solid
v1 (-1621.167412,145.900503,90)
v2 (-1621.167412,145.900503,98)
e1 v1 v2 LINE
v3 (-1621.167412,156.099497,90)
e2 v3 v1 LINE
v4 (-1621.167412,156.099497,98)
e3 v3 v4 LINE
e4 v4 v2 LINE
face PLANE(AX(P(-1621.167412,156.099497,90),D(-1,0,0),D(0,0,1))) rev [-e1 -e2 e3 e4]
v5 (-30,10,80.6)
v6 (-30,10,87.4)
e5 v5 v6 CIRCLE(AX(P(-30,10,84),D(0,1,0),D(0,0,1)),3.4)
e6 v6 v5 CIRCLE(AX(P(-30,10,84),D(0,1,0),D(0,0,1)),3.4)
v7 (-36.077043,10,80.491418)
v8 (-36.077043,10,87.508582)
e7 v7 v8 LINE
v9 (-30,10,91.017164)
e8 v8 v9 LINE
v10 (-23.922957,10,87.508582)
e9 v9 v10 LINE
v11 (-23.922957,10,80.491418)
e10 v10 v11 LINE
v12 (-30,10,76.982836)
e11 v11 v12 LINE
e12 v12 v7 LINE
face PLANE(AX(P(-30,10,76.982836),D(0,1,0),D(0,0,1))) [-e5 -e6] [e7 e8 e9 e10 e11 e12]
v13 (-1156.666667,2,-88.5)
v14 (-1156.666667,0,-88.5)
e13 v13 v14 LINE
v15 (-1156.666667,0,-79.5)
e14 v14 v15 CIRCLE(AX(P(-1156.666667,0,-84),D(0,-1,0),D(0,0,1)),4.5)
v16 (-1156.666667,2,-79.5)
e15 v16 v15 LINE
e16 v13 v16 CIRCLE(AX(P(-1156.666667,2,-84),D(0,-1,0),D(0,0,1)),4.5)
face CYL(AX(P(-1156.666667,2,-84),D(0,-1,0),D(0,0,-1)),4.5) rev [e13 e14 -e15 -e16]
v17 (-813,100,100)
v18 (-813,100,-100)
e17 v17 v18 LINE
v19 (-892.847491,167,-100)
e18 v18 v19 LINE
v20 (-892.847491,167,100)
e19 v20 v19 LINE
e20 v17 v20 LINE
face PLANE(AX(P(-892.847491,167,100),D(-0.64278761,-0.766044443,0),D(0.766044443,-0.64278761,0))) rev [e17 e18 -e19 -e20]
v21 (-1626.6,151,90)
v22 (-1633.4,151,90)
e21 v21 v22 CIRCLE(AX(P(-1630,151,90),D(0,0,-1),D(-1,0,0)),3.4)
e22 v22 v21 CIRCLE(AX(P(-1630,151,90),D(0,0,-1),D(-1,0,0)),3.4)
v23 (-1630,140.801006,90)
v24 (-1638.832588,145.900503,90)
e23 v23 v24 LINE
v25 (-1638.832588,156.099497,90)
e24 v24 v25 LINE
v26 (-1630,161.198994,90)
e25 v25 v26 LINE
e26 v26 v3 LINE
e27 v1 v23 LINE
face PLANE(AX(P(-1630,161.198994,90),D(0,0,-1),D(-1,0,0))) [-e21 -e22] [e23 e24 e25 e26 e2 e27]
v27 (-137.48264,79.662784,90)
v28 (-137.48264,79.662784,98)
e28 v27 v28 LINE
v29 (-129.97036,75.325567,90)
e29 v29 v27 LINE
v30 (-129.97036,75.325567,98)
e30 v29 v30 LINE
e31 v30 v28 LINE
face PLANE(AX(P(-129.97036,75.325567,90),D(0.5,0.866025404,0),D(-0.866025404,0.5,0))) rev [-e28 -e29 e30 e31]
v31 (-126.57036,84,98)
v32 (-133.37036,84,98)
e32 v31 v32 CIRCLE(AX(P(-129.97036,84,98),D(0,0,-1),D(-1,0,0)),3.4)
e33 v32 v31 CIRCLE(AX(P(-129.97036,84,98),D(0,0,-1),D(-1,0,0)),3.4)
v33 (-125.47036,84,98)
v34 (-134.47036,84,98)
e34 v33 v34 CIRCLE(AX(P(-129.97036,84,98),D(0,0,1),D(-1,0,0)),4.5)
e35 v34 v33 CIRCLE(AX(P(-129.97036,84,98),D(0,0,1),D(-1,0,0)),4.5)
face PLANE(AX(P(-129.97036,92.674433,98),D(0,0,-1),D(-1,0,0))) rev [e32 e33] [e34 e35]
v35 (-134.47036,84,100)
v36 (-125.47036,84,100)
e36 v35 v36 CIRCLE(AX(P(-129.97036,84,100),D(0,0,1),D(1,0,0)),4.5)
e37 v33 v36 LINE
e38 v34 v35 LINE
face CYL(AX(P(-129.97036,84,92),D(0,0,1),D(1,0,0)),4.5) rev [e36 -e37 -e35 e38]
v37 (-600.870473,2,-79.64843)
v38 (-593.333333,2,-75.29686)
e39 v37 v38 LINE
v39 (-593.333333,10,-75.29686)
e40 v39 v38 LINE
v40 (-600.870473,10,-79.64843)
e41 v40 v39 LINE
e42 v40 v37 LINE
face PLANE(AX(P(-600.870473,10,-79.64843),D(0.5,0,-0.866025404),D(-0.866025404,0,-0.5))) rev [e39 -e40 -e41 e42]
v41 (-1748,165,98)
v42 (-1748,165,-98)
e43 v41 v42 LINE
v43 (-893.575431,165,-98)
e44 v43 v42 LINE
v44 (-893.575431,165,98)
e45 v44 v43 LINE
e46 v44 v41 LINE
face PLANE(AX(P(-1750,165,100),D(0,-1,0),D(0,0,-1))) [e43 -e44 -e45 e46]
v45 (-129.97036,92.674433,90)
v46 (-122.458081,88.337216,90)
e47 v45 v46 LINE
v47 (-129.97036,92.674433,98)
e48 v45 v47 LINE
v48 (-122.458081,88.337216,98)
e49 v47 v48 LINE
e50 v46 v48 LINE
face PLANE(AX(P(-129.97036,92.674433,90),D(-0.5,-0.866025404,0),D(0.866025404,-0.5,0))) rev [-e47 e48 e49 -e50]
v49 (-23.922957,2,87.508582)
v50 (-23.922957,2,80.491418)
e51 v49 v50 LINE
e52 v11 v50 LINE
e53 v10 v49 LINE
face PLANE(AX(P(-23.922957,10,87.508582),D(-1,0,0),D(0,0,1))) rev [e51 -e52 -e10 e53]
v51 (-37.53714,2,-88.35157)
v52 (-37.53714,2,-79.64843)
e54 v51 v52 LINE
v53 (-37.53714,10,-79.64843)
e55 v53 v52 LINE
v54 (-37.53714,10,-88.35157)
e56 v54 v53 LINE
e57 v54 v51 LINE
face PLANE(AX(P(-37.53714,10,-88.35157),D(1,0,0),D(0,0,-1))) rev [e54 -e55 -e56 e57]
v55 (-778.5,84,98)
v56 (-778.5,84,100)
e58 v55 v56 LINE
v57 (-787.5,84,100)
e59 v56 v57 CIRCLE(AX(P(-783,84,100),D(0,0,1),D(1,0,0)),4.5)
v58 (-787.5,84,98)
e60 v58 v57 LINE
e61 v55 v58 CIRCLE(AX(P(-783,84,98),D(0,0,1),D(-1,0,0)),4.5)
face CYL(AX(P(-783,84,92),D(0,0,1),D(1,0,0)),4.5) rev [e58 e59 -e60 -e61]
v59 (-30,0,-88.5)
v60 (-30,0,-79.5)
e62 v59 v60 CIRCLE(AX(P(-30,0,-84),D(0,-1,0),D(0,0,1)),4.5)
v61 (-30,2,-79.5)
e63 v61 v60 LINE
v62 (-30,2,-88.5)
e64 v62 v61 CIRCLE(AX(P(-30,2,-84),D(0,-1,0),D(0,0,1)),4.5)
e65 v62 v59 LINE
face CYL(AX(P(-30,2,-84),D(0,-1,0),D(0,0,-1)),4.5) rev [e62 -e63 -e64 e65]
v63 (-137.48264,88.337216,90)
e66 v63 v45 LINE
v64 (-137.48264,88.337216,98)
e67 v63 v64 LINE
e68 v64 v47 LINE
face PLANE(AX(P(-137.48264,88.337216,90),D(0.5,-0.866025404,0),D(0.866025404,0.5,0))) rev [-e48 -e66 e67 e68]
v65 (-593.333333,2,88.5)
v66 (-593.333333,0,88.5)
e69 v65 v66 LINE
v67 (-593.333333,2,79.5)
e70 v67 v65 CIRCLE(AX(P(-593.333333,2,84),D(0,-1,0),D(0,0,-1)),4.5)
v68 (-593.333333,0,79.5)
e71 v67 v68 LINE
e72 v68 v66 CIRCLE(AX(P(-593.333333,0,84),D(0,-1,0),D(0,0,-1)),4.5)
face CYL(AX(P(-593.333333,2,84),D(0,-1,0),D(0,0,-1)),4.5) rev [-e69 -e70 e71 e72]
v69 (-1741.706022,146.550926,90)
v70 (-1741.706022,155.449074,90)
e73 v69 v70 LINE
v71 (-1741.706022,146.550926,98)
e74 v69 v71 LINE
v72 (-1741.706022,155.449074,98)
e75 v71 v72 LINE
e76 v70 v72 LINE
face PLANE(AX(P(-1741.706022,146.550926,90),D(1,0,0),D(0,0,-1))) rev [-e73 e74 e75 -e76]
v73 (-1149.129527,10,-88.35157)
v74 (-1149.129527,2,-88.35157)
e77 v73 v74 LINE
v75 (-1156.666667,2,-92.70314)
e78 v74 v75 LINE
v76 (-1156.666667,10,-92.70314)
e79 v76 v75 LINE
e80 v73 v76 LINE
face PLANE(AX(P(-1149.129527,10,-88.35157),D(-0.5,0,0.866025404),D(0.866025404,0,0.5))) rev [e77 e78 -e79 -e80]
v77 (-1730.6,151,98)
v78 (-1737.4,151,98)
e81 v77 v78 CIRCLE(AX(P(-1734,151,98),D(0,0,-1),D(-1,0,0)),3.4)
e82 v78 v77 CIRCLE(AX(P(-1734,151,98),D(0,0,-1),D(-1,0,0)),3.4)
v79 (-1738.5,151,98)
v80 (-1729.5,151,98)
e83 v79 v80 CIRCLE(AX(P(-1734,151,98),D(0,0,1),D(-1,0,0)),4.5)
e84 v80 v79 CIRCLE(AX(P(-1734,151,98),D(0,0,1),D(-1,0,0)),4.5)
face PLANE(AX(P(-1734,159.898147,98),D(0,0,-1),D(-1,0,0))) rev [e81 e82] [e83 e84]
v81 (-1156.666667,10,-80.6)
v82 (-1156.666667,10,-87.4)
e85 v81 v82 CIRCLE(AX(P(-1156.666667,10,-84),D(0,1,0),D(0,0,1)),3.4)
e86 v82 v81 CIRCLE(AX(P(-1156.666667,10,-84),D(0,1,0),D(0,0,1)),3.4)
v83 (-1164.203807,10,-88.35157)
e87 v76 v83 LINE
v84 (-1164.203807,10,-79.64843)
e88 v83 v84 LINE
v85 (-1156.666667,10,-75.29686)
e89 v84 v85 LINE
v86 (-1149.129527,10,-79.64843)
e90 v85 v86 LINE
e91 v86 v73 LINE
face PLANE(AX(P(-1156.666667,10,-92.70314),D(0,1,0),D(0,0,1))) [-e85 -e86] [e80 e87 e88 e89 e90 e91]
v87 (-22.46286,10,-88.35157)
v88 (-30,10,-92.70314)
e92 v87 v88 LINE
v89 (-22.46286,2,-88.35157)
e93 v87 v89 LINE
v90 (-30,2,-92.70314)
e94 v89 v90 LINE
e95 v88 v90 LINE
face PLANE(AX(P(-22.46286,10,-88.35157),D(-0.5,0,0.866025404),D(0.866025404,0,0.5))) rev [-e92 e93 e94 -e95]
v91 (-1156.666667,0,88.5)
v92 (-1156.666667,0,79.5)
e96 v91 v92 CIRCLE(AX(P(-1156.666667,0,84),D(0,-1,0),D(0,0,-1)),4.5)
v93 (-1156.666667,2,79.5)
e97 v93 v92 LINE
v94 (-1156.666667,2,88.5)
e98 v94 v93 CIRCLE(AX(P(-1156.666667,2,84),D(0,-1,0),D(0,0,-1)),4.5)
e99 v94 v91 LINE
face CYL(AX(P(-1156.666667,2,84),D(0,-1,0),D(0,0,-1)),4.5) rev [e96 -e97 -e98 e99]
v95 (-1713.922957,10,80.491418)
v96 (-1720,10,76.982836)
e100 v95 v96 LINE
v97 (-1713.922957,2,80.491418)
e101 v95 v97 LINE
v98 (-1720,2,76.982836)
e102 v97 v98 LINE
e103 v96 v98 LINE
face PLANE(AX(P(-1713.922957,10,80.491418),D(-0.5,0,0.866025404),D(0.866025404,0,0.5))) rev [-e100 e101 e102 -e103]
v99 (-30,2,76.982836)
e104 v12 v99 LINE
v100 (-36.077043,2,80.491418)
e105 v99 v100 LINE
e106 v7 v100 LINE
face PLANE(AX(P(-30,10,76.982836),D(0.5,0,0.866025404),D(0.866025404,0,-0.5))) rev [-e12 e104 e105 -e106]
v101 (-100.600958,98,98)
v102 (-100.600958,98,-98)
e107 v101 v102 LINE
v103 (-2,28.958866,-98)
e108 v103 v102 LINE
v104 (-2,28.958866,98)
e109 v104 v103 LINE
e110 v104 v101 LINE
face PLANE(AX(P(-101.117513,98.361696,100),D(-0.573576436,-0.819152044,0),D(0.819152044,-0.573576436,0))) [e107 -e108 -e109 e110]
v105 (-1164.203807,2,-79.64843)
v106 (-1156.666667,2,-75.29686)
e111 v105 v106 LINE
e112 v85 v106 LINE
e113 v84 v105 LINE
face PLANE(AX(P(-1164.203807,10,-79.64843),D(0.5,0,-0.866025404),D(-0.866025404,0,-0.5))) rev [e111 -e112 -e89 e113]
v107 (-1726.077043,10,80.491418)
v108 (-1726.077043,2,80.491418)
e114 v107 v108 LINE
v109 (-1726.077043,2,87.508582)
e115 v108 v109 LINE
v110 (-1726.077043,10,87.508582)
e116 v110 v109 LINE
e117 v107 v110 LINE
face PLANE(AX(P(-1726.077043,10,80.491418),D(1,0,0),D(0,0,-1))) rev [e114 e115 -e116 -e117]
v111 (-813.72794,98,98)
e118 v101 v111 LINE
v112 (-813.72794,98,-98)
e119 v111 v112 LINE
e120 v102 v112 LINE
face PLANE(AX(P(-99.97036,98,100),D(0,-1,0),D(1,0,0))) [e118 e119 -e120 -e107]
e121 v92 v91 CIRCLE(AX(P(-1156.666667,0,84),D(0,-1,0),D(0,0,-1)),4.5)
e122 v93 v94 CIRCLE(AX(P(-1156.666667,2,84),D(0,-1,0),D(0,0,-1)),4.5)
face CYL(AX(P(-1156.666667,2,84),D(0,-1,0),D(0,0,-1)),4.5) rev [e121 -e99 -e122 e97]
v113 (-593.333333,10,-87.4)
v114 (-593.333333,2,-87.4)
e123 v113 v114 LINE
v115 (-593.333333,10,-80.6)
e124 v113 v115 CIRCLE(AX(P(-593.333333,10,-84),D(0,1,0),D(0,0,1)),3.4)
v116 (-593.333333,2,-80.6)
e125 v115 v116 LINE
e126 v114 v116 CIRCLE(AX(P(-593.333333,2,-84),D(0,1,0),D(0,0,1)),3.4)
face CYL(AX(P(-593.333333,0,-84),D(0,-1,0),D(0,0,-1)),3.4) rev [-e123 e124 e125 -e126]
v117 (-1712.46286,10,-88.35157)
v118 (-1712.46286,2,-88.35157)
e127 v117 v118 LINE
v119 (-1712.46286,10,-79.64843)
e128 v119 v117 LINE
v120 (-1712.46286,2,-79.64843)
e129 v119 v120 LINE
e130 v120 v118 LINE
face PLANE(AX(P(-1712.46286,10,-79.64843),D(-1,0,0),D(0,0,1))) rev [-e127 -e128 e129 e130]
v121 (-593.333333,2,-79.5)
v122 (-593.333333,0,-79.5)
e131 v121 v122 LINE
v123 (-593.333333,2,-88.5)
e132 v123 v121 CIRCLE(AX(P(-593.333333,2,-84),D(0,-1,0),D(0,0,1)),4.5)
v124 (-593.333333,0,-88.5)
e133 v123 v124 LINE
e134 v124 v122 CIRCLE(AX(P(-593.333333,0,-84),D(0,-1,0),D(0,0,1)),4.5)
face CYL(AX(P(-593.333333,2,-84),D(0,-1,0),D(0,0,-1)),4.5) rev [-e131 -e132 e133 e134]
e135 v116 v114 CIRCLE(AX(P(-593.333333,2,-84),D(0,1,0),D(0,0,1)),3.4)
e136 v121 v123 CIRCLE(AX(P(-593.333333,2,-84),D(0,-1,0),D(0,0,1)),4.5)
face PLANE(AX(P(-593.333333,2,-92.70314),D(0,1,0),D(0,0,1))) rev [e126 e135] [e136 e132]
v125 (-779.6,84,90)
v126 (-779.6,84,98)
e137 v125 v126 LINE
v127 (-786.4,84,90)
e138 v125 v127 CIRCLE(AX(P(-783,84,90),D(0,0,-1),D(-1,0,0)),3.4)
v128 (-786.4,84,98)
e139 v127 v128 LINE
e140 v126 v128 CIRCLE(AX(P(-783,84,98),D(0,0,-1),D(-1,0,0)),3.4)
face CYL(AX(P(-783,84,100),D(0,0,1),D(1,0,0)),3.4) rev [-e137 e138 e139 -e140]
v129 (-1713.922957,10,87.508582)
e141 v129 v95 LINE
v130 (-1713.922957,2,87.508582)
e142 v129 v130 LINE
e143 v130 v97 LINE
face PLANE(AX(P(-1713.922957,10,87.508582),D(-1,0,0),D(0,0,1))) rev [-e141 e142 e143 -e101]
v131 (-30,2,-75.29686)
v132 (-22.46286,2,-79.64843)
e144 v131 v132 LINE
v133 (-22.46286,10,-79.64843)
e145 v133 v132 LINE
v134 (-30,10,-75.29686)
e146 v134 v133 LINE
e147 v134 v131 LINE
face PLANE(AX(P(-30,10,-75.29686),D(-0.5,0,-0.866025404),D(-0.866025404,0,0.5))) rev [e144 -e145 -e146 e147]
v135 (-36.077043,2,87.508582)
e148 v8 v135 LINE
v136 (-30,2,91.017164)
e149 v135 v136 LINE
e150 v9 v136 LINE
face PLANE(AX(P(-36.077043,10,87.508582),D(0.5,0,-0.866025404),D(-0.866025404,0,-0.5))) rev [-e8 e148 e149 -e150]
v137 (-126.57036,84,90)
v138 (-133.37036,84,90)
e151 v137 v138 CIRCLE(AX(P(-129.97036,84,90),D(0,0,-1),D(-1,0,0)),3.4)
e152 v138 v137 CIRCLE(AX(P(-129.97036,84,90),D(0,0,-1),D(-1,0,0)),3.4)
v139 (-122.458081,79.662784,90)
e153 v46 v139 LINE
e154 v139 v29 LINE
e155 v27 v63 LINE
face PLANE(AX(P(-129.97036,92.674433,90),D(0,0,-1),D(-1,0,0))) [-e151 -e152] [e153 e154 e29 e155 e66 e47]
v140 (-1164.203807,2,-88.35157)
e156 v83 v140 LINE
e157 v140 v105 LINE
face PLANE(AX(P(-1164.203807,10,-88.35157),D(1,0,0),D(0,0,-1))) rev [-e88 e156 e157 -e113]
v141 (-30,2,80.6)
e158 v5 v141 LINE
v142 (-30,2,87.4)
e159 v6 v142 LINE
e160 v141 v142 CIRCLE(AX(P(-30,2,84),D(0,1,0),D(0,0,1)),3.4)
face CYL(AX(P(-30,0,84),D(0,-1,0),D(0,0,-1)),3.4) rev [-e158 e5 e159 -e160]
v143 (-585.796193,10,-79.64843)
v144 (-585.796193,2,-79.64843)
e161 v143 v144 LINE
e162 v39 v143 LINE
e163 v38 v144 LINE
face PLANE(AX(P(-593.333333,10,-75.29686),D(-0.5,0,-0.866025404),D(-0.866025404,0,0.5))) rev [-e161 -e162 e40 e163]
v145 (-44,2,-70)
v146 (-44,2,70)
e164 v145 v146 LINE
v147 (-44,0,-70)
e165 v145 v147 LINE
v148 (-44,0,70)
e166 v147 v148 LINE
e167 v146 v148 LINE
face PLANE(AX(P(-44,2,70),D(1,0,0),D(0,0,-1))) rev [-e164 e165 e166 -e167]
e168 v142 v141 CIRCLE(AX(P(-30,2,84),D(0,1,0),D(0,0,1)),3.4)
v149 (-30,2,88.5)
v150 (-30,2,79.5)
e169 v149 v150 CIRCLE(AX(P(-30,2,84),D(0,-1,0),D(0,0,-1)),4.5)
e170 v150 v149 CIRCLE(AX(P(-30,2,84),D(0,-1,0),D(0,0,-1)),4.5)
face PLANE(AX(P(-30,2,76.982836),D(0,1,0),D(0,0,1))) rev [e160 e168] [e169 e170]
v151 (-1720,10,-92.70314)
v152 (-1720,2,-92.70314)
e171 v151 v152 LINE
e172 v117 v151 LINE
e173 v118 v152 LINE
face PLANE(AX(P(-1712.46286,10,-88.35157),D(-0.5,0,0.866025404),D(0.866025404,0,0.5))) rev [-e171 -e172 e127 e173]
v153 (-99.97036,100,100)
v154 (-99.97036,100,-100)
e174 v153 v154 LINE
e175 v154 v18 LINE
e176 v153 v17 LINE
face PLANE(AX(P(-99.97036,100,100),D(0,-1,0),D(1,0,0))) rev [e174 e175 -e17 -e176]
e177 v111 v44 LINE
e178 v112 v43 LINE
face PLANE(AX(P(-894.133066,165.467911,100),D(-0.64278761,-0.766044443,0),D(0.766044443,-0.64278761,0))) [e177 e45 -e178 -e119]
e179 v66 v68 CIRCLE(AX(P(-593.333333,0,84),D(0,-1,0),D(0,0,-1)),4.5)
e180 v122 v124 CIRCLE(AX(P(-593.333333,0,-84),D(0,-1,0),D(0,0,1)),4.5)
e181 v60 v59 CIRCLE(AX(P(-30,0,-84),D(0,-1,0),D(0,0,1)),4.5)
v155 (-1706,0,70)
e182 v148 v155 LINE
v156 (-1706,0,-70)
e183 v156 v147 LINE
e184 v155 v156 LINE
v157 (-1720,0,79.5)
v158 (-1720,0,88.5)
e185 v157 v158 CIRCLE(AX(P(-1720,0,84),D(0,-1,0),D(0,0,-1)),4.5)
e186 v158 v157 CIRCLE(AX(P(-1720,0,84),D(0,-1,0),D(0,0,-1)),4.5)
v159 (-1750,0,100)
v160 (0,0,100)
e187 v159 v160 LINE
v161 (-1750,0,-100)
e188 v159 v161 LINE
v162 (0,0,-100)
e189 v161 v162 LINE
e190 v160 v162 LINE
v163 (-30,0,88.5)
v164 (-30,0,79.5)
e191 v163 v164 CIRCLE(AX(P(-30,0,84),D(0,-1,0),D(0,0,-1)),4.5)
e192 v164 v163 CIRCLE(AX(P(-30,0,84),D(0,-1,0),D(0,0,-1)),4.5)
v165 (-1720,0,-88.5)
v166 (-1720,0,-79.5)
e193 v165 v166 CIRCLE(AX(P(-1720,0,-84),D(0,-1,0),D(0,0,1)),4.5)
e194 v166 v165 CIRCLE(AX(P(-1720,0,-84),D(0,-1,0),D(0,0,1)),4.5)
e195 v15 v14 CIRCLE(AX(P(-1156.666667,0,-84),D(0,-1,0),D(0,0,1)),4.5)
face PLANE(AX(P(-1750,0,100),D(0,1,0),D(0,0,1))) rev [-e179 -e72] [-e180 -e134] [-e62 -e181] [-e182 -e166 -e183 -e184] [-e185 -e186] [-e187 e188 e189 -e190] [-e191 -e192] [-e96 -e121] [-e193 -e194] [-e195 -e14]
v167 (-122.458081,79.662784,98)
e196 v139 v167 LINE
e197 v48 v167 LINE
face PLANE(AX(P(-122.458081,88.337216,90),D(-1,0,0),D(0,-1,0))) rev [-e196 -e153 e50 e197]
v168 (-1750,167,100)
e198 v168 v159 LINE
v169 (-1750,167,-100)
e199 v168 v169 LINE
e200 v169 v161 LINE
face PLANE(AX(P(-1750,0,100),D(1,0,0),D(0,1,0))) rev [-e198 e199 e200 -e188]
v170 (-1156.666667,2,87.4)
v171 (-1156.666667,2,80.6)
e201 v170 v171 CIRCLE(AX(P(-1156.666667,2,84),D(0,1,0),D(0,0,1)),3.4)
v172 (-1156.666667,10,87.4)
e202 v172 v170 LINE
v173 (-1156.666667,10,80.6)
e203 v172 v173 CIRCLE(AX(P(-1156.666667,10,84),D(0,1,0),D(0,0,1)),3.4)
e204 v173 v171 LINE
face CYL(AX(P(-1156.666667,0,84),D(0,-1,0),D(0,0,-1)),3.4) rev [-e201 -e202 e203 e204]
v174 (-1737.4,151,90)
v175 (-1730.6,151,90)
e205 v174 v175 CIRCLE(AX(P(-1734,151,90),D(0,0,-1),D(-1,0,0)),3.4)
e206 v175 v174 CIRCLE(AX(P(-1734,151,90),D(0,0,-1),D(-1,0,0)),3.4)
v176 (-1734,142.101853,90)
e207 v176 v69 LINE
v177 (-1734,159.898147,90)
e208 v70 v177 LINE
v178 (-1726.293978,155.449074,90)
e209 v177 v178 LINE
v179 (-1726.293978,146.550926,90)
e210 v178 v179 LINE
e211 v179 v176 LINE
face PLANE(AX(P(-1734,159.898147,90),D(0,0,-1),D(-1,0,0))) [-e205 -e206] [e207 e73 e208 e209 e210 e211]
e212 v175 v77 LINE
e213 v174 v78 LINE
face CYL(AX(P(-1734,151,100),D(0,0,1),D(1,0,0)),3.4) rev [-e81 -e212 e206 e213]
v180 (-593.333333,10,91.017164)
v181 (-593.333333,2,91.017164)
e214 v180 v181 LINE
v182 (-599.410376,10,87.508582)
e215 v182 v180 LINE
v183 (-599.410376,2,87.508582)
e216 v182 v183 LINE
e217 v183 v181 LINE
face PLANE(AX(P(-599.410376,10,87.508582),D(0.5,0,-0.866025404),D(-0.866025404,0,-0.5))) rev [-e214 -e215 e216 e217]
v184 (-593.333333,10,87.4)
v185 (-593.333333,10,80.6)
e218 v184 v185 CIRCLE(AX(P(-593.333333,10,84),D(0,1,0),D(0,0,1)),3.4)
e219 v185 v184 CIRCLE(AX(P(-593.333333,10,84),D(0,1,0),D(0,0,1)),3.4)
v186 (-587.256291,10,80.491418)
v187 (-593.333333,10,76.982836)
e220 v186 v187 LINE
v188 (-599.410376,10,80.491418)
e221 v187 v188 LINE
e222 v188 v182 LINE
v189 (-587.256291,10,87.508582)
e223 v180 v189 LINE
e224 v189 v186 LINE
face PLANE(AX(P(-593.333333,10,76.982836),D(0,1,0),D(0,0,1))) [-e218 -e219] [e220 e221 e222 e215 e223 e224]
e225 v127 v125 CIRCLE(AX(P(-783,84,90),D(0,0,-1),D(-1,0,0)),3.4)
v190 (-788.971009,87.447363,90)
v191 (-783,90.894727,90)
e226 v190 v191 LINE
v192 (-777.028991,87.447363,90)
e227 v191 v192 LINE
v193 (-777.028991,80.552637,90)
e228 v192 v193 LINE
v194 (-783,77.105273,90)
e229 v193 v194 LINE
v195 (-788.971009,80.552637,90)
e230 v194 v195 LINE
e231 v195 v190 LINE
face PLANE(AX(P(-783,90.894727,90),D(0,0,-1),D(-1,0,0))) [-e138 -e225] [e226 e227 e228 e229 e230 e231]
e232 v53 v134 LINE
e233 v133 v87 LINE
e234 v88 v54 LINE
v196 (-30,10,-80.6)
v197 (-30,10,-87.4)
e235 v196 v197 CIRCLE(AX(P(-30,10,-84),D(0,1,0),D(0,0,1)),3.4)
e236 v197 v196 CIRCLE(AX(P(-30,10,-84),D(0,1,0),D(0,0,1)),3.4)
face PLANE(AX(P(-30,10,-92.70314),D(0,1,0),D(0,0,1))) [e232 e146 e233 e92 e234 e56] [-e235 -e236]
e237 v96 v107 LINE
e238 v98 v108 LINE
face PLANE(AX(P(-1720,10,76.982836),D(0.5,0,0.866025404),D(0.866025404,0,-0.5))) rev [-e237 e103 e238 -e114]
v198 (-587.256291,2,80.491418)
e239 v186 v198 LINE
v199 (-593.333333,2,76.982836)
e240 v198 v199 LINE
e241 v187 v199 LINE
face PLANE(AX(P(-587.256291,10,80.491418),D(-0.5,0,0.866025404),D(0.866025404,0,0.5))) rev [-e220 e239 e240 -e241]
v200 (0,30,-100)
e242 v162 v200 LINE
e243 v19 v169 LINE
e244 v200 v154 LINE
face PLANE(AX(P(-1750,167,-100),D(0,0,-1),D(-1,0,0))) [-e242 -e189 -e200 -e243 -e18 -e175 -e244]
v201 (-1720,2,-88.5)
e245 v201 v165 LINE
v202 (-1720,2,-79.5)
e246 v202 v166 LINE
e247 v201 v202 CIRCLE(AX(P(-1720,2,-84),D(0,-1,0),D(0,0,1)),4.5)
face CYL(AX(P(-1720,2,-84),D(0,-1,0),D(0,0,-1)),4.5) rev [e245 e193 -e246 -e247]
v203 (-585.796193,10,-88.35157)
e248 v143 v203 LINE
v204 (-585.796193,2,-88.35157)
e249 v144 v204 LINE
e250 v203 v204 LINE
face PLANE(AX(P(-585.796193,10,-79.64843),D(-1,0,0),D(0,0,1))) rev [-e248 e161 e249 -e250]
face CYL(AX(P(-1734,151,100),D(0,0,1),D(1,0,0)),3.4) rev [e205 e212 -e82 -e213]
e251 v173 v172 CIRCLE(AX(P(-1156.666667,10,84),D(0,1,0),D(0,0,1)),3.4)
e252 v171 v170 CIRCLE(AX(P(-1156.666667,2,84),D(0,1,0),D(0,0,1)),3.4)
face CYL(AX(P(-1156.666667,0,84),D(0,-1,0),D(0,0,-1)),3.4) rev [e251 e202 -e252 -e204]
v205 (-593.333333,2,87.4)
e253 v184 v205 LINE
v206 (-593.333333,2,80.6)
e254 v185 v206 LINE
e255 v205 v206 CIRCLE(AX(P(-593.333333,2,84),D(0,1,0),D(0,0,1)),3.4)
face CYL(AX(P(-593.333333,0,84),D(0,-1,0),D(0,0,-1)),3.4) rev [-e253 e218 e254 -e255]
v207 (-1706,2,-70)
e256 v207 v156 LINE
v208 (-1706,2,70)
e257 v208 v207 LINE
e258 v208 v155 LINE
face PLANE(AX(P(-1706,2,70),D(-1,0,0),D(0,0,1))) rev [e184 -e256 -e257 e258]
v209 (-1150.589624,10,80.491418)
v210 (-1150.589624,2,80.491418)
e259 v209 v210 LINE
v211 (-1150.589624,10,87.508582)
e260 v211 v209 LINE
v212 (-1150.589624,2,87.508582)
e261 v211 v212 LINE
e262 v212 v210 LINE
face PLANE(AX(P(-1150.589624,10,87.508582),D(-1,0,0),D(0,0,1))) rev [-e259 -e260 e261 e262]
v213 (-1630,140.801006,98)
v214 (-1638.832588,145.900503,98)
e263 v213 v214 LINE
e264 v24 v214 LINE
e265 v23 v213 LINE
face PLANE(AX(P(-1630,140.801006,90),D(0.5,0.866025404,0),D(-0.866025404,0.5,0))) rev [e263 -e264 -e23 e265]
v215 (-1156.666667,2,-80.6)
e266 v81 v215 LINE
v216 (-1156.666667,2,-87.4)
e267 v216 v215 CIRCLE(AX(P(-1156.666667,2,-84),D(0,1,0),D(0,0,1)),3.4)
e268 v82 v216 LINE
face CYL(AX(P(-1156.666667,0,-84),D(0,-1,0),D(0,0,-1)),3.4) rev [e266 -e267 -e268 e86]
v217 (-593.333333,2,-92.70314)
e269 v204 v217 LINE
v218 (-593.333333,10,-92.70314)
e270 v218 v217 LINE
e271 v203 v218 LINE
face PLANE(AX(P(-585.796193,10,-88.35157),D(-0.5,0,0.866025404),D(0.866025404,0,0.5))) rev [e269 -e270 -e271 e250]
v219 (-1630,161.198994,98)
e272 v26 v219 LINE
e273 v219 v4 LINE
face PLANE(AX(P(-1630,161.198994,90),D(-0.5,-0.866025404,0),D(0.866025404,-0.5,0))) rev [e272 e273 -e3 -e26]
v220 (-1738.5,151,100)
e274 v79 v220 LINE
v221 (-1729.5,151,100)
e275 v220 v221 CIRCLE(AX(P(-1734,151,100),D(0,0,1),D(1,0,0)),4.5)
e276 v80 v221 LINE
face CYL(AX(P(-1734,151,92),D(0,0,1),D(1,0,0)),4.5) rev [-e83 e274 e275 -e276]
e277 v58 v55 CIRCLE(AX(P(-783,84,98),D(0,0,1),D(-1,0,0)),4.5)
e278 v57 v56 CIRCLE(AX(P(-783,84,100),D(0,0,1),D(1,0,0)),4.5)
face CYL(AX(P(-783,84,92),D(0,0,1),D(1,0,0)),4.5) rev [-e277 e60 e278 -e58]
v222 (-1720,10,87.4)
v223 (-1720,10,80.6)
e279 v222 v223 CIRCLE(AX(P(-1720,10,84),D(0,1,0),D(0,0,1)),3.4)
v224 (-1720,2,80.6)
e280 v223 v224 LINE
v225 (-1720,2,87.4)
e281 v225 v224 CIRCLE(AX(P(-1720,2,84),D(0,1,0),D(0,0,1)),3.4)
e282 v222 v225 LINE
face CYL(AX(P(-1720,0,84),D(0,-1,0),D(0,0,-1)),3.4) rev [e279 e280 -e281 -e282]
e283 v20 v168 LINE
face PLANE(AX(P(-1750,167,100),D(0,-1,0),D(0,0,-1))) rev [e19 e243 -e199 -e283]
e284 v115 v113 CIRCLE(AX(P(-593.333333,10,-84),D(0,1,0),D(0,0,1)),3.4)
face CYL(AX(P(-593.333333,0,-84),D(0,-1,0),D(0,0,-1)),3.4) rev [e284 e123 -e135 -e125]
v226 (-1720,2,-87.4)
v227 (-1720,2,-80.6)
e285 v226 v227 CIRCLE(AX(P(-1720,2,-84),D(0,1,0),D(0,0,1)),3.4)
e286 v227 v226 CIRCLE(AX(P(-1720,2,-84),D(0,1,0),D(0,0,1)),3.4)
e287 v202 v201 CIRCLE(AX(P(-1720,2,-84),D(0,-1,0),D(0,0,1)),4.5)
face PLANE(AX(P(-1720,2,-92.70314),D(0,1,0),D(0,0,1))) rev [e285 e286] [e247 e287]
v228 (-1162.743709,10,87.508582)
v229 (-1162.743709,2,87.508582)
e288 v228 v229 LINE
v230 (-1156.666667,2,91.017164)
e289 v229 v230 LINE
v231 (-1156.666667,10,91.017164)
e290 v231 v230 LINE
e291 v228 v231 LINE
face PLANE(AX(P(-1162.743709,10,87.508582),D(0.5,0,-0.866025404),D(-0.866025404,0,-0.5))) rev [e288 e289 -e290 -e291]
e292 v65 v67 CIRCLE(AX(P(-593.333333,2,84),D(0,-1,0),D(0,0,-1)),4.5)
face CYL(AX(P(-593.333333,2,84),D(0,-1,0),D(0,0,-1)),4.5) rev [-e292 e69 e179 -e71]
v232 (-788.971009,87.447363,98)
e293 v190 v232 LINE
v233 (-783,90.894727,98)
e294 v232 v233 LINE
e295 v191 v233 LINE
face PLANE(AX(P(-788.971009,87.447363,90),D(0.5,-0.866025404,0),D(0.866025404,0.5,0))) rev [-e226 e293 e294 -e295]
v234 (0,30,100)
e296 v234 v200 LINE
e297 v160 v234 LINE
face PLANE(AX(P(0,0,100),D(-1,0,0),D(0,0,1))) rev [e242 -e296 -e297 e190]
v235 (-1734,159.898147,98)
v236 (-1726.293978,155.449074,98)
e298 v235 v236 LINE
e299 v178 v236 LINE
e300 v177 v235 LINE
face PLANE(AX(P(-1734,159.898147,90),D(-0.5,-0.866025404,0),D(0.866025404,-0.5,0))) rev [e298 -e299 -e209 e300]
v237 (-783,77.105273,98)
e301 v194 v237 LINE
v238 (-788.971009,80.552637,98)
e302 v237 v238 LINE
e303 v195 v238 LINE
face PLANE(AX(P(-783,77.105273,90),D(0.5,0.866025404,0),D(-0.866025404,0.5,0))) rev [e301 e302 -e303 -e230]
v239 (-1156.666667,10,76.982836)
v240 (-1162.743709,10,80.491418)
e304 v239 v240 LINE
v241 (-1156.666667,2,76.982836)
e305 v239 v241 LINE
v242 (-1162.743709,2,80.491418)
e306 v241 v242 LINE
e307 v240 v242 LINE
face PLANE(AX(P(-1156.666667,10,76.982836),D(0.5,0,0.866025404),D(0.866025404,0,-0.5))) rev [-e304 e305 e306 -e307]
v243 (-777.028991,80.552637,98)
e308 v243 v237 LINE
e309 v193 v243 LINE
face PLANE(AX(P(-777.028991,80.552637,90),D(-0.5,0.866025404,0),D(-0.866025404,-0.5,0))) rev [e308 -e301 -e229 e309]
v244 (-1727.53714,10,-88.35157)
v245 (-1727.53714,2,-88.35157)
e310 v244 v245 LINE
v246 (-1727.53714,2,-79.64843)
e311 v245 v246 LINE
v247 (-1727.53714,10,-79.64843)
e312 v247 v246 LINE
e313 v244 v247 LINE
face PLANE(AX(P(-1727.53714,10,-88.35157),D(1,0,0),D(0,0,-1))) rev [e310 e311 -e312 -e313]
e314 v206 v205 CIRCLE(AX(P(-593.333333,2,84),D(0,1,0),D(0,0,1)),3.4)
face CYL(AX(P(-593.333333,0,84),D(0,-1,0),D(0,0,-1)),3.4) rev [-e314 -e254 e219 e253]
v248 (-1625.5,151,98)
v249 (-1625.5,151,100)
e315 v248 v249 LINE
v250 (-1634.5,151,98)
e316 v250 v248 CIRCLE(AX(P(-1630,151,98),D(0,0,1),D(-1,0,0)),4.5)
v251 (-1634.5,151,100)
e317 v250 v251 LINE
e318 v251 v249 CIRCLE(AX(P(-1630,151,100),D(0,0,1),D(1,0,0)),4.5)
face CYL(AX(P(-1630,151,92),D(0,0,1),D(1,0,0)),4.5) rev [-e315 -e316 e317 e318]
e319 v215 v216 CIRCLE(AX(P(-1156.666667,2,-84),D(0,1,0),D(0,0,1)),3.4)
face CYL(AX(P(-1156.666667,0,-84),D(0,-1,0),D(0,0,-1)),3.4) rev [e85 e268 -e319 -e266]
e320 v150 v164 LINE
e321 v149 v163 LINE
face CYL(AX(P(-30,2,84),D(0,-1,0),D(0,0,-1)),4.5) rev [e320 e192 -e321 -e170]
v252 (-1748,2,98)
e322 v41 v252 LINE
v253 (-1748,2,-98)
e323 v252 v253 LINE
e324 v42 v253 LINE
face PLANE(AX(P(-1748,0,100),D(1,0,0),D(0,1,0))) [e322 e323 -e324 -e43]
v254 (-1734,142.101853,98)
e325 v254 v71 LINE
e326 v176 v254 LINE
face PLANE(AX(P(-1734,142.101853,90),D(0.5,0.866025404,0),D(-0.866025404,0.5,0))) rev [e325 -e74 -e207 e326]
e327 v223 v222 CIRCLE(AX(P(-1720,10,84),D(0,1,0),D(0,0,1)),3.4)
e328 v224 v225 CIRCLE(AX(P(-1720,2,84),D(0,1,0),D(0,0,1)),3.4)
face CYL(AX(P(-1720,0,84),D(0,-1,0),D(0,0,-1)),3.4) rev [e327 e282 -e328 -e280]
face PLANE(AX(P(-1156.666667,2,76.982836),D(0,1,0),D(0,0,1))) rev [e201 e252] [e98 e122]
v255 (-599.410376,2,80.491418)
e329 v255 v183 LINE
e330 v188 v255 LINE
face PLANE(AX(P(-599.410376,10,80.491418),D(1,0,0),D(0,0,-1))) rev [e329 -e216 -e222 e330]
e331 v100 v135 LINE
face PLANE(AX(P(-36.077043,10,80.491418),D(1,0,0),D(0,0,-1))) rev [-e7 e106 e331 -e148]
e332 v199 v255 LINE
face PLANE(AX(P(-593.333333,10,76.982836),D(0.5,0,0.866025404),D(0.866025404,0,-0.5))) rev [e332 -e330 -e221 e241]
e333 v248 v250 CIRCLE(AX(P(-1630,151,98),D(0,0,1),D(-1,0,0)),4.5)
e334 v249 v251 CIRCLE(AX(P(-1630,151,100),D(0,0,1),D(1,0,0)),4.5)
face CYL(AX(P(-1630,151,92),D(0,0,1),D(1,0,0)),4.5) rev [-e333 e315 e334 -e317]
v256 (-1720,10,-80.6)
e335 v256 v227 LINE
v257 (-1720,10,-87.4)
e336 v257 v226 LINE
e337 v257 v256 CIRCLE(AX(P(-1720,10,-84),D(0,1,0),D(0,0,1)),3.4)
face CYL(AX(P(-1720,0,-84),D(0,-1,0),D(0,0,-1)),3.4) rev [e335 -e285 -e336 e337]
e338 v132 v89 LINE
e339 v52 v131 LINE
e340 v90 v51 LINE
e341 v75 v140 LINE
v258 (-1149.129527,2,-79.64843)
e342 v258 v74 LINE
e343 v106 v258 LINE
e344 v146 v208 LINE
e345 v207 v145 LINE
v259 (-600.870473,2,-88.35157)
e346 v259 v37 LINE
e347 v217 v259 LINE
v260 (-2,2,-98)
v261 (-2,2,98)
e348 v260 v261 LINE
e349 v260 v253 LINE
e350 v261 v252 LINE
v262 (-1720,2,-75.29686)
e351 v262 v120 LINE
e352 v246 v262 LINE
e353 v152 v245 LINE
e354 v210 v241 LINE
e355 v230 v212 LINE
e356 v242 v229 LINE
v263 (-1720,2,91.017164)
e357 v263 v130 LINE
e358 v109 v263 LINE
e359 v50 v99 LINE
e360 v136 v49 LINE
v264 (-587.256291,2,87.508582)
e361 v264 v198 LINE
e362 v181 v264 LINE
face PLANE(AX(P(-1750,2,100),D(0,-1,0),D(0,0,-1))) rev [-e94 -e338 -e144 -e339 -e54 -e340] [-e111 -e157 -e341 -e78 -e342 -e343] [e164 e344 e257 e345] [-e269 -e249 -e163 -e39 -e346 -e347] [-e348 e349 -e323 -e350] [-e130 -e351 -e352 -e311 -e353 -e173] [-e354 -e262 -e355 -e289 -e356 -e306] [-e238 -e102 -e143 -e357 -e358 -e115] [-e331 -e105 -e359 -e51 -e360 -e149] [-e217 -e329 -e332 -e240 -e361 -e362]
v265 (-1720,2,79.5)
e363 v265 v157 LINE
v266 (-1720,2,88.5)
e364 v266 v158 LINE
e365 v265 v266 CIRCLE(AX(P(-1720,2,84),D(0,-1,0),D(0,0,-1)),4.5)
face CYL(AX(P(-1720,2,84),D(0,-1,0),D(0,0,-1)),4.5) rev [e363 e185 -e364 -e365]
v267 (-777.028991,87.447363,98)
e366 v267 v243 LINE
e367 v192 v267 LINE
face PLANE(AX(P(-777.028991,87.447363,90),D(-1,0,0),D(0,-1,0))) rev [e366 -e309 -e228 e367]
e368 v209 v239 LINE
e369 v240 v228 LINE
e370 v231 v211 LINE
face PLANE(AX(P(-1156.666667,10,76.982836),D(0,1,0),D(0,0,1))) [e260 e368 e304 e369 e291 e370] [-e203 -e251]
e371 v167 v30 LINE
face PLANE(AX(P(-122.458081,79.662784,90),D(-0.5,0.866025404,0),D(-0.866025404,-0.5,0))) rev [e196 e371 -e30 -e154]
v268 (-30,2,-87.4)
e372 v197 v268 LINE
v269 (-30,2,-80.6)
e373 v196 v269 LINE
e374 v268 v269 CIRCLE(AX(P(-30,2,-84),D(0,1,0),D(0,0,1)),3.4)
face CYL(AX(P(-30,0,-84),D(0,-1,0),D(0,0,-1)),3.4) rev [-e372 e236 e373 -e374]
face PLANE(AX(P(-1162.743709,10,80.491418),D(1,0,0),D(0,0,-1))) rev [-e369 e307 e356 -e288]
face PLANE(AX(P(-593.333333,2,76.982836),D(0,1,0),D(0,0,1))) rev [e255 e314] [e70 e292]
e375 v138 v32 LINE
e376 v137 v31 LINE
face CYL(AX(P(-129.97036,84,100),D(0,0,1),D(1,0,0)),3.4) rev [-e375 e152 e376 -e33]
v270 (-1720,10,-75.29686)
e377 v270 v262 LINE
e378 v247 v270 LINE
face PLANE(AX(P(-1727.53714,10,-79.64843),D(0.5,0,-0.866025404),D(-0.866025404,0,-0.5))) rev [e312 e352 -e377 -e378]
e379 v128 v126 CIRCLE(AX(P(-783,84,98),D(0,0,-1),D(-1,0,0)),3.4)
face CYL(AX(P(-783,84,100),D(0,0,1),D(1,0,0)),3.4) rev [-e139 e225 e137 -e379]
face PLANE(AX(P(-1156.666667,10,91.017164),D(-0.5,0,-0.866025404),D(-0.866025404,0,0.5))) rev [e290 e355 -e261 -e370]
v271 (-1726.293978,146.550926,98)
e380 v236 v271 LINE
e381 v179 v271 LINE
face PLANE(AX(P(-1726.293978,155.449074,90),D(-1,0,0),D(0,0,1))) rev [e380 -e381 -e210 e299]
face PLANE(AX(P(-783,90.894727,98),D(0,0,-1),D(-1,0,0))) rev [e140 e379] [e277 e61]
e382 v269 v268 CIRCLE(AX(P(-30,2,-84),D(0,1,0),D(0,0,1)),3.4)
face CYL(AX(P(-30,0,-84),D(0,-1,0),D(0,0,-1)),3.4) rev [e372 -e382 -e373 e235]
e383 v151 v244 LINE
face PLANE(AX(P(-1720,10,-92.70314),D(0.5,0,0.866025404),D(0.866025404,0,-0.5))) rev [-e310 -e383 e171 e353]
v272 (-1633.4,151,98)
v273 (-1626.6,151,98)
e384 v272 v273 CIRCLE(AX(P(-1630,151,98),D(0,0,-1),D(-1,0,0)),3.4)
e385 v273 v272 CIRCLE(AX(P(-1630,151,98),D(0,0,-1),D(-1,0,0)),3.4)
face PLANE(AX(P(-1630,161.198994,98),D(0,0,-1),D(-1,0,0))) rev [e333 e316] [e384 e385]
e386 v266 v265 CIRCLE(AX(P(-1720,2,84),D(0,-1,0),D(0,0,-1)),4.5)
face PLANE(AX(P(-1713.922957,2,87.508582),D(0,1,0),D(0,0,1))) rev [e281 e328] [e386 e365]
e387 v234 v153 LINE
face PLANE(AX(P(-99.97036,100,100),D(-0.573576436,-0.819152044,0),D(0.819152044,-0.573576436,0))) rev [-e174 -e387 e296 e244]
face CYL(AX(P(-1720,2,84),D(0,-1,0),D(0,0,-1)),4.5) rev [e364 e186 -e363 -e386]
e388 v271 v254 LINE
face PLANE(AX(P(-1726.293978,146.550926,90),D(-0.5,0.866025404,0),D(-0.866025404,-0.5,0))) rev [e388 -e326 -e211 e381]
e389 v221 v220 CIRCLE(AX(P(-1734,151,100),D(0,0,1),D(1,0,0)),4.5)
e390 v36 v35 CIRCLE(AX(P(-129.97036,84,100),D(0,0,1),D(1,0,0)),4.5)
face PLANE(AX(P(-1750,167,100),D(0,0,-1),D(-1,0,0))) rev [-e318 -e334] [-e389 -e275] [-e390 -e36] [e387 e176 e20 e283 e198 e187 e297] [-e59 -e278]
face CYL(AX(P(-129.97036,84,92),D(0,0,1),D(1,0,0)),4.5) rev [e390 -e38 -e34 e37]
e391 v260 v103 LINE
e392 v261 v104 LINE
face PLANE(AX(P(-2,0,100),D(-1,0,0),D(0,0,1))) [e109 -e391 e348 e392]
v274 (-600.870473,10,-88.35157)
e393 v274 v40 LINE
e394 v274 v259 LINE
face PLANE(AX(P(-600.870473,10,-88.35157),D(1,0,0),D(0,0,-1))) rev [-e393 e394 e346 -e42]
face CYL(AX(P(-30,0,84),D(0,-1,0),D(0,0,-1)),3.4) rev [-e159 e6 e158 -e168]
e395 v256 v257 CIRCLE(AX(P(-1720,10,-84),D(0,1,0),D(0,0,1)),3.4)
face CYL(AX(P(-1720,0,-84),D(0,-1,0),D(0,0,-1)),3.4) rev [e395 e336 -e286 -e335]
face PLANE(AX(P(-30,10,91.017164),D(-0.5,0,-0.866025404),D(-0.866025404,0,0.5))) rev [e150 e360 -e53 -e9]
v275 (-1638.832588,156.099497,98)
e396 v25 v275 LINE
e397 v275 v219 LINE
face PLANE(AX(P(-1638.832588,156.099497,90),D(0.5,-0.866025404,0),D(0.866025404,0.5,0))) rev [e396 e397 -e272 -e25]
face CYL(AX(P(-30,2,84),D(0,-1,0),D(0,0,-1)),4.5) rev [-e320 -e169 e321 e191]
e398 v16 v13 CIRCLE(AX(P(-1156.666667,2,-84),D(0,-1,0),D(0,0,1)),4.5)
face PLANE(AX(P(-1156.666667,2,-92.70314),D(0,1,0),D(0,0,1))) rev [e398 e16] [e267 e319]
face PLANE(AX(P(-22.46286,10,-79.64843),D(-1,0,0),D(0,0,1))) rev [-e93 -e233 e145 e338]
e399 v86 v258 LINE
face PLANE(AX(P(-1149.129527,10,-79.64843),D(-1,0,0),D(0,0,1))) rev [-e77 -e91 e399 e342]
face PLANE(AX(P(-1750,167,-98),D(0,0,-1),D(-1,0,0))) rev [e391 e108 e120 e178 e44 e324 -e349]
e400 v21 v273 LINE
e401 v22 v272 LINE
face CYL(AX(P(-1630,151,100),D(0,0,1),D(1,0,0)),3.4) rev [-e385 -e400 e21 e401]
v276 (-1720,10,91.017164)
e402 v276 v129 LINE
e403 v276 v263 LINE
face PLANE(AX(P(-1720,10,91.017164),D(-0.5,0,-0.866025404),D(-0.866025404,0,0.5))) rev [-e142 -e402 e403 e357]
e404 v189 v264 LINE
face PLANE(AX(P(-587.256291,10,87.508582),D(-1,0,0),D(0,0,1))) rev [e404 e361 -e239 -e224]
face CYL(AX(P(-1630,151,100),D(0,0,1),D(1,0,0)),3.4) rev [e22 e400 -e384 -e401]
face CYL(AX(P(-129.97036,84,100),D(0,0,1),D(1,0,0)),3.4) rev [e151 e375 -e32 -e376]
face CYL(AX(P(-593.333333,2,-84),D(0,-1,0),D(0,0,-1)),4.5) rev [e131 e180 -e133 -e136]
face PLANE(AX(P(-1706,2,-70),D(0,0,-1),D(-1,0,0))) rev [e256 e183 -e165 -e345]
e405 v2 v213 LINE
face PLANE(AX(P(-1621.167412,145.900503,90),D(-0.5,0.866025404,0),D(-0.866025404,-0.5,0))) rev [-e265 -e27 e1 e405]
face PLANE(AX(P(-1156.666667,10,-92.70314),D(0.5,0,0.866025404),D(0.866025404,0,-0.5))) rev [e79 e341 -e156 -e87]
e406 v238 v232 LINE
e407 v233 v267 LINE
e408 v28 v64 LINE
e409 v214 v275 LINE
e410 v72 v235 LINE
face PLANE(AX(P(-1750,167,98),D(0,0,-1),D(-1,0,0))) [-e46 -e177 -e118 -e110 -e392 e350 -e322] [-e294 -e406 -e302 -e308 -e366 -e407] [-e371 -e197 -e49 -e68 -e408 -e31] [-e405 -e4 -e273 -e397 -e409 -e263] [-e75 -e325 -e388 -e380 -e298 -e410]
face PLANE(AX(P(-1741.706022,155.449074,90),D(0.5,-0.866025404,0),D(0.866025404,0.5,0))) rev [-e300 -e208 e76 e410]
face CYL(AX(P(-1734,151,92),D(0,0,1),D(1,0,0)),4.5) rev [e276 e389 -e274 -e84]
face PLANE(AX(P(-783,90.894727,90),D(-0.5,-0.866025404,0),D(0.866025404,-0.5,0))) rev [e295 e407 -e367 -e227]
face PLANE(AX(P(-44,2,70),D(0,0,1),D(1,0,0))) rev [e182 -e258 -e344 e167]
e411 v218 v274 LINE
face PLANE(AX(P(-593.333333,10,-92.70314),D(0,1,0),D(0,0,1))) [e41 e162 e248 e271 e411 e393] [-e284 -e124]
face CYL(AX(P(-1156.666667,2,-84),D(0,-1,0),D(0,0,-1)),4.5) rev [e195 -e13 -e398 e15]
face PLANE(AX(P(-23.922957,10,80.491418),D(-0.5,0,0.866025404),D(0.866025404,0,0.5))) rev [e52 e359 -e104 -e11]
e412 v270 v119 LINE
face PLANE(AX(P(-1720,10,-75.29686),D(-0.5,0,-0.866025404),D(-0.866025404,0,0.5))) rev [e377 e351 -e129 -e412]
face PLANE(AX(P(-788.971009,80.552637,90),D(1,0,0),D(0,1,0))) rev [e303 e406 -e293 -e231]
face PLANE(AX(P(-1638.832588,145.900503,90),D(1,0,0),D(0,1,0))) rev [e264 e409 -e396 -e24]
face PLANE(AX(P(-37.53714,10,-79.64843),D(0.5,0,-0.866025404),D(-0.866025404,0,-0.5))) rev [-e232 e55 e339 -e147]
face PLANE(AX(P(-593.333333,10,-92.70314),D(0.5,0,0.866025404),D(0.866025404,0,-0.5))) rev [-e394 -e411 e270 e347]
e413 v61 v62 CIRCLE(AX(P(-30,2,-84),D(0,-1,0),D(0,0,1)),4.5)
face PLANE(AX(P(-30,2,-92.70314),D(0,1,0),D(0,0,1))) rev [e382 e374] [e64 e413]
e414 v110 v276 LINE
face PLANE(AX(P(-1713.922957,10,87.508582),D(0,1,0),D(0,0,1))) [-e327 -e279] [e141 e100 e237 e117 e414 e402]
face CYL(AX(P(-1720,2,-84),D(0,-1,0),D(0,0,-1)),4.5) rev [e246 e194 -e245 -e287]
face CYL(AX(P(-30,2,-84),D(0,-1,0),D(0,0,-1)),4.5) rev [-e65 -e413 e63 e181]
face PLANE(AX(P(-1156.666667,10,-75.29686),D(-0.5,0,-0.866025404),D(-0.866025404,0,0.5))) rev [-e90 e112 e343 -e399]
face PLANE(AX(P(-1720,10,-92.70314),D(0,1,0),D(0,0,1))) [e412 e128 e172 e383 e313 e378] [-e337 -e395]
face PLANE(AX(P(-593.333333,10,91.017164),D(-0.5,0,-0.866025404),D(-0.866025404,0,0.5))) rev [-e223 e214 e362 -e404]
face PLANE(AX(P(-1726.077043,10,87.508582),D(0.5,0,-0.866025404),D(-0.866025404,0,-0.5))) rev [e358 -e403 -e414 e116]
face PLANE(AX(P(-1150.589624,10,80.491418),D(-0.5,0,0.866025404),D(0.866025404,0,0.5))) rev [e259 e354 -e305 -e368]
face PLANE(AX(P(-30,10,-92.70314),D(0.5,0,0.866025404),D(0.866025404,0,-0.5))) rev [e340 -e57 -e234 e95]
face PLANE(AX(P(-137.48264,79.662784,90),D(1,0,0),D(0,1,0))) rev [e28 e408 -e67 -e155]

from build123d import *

# Parameters (mm, degrees)
EXTRUDE_1_DEPTH        = 100
SHELL_1_T              = -2
SKETCH_2_W             = 1750
SKETCH_2_H             = 200
SKETCH_2_W_2           = 1662
SKETCH_2_H_2           = 140
EXTRUDE_2_DEPTH        = 2
SKETCH_3_R             = 4.5
CUT_EXTRUDE_1_DEPTH    = 2
EXTRUDE_4_DEPTH        = 8
HOLE_WIZARD_M8_1_D     = 6.8
HOLE_WIZARD_M8_1_DEPTH = 19.75
HOLE_WIZARD_M8_1_TIP   = 2.042926105
SKETCH_8_R             = 4.5
CUT_EXTRUDE_2_DEPTH    = 8
EXTRUDE_5_DEPTH        = 8
HOLE_WIZARD_M8_2_D     = 6.8
HOLE_WIZARD_M8_2_DEPTH = 19.75
HOLE_WIZARD_M8_2_TIP   = 2.042926105


with BuildPart() as part:
    # 草图1 → 凸台-拉伸1 (new, symmetric)
    with BuildSketch(Plane.XY):
        Polygon((-1750, 0), (0, 0), (0, 30), (-99.970360472, 100), (-813, 100), (-892.847490704, 167), (-1750, 167), align=None)
    extrude(amount=EXTRUDE_1_DEPTH, both=True)

    # 抽壳1
    shell_1_openings = [part.faces().sort_by_distance(p)[0] for p in [
        (-875, 0, 0),
    ]]
    offset(amount=SHELL_1_T, openings=shell_1_openings, kind=Kind.INTERSECTION)

    # 草图2 → 凸台-拉伸2 (add)
    with BuildSketch(Plane.XZ):
        with Locations((-875, 0)):
            Rectangle(SKETCH_2_W, SKETCH_2_H)
        with Locations((-875, 0)):
            Rectangle(SKETCH_2_W_2, SKETCH_2_H_2, mode=Mode.SUBTRACT)
    extrude(amount=-EXTRUDE_2_DEPTH)

    # 草图3 → 切除-拉伸1 (cut)
    with BuildSketch(Plane.XZ):
        with Locations(Location((-1720, 84, 0), (0, 0, 270))):
            Circle(SKETCH_3_R)
        with Locations(Location((-1156.666666667, 84, 0), (0, 0, 270))):
            Circle(SKETCH_3_R)
        with Locations(Location((-593.333333333, 84, 0), (0, 0, 270))):
            Circle(SKETCH_3_R)
        with Locations(Location((-30, 84, 0), (0, 0, 270))):
            Circle(SKETCH_3_R)
        with Locations(Location((-30, -84, 0), (0, 0, 90))):
            Circle(SKETCH_3_R)
        with Locations(Location((-593.333333333, -84, 0), (0, 0, 90))):
            Circle(SKETCH_3_R)
        with Locations(Location((-1156.666666667, -84, 0), (0, 0, 90))):
            Circle(SKETCH_3_R)
        with Locations(Location((-1720, -84, 0), (0, 0, 90))):
            Circle(SKETCH_3_R)
    extrude(amount=-CUT_EXTRUDE_1_DEPTH, mode=Mode.SUBTRACT)

    # 草图4 → 凸台-拉伸4 (add)
    with BuildSketch(Plane(origin=(0, 2, 0), x_dir=(1, 0, 0), z_dir=(0, 1, 0))):
        Polygon((-1713.922957331, -87.508582221), (-1713.922957331, -80.491417779), (-1720, -76.982835559), (-1726.077042669, -80.491417779), (-1726.077042669, -87.508582221), (-1720, -91.017164441), align=None)
        Polygon((-1720, 92.703139603), (-1727.537139989, 88.351569801), (-1727.537139989, 79.648430199), (-1720, 75.296860397), (-1712.462860011, 79.648430199), (-1712.462860011, 88.351569801), align=None)
        Polygon((-1156.666666667, 92.703139603), (-1164.203806655, 88.351569801), (-1164.203806655, 79.648430199), (-1156.666666667, 75.296860397), (-1149.129526678, 79.648430199), (-1149.129526678, 88.351569801), align=None)
        Polygon((-1156.666666667, -76.982835559), (-1162.743709335, -80.491417779), (-1162.743709335, -87.508582221), (-1156.666666667, -91.017164441), (-1150.589623998, -87.508582221), (-1150.589623998, -80.491417779), align=None)
        Polygon((-593.333333333, -76.982835559), (-599.410376002, -80.491417779), (-599.410376002, -87.508582221), (-593.333333333, -91.017164441), (-587.256290665, -87.508582221), (-587.256290665, -80.491417779), align=None)
        Polygon((-30, -76.982835559), (-36.077042669, -80.491417779), (-36.077042669, -87.508582221), (-30, -91.017164441), (-23.922957331, -87.508582221), (-23.922957331, -80.491417779), align=None)
        Polygon((-30, 92.703139603), (-37.537139989, 88.351569801), (-37.537139989, 79.648430199), (-30, 75.296860397), (-22.462860011, 79.648430199), (-22.462860011, 88.351569801), align=None)
        Polygon((-593.333333333, 92.703139603), (-600.870473322, 88.351569801), (-600.870473322, 79.648430199), (-593.333333333, 75.296860397), (-585.796193345, 79.648430199), (-585.796193345, 88.351569801), align=None)
    extrude(amount=EXTRUDE_4_DEPTH)

    # M8 螺纹孔1
    with Locations(Plane.XZ):
        with Locations((-1720, 84), (-1720, -84), (-1156.666666667, -84), (-1156.666666667, 84), (-593.333333333, 84), (-593.333333333, -84), (-30, 84), (-30, -84)):
            Hole(HOLE_WIZARD_M8_1_D / 2, depth=HOLE_WIZARD_M8_1_DEPTH)
            with Locations((0, 0, -(HOLE_WIZARD_M8_1_DEPTH + HOLE_WIZARD_M8_1_TIP / 2))):  # 118° drill point
                Cone(0, HOLE_WIZARD_M8_1_D / 2, HOLE_WIZARD_M8_1_TIP, mode=Mode.SUBTRACT)

    # 草图8 → 切除-拉伸2 (cut)
    with BuildSketch(Plane.XY.offset(100)):
        with Locations((-1734, 151)):
            Circle(SKETCH_8_R)
        with Locations((-1630, 151)):
            Circle(SKETCH_8_R)
        with Locations((-783, 84)):
            Circle(SKETCH_8_R)
        with Locations((-129.970360472, 84)):
            Circle(SKETCH_8_R)
    extrude(amount=-CUT_EXTRUDE_2_DEPTH, mode=Mode.SUBTRACT)

    # 草图9 → 凸台-拉伸5 (add)
    with BuildSketch(Plane(origin=(0, 0, 98), x_dir=(-1, 0, 0), z_dir=(0, 0, -1))):
        Polygon((1630, 161.198993807), (1621.16741227, 156.099496903), (1621.16741227, 145.900503097), (1630, 140.801006193), (1638.83258773, 145.900503097), (1638.83258773, 156.099496903), align=None)
        Polygon((1734, 159.898147478), (1726.293978237, 155.449073739), (1726.293978237, 146.550926261), (1734, 142.101852522), (1741.706021763, 146.550926261), (1741.706021763, 155.449073739), align=None)
        Polygon((783, 90.89472697), (777.028991292, 87.447363485), (777.028991292, 80.552636515), (783, 77.10527303), (788.971008708, 80.552636515), (788.971008708, 87.447363485), align=None)
        Polygon((129.970360472, 92.674432694), (122.458081396, 88.337216347), (122.458081396, 79.662783653), (129.970360472, 75.325567306), (137.482639548, 79.662783653), (137.482639548, 88.337216347), align=None)
    extrude(amount=EXTRUDE_5_DEPTH)

    # M8 螺纹孔2
    with Locations(Plane.XY.offset(100)):
        with Locations((-1630, 151), (-1734, 151), (-783, 84), (-129.970360472, 84)):
            Hole(HOLE_WIZARD_M8_2_D / 2, depth=HOLE_WIZARD_M8_2_DEPTH)
            with Locations((0, 0, -(HOLE_WIZARD_M8_2_DEPTH + HOLE_WIZARD_M8_2_TIP / 2))):  # 118° drill point
                Cone(0, HOLE_WIZARD_M8_2_D / 2, HOLE_WIZARD_M8_2_TIP, mode=Mode.SUBTRACT)


solid = part.part
